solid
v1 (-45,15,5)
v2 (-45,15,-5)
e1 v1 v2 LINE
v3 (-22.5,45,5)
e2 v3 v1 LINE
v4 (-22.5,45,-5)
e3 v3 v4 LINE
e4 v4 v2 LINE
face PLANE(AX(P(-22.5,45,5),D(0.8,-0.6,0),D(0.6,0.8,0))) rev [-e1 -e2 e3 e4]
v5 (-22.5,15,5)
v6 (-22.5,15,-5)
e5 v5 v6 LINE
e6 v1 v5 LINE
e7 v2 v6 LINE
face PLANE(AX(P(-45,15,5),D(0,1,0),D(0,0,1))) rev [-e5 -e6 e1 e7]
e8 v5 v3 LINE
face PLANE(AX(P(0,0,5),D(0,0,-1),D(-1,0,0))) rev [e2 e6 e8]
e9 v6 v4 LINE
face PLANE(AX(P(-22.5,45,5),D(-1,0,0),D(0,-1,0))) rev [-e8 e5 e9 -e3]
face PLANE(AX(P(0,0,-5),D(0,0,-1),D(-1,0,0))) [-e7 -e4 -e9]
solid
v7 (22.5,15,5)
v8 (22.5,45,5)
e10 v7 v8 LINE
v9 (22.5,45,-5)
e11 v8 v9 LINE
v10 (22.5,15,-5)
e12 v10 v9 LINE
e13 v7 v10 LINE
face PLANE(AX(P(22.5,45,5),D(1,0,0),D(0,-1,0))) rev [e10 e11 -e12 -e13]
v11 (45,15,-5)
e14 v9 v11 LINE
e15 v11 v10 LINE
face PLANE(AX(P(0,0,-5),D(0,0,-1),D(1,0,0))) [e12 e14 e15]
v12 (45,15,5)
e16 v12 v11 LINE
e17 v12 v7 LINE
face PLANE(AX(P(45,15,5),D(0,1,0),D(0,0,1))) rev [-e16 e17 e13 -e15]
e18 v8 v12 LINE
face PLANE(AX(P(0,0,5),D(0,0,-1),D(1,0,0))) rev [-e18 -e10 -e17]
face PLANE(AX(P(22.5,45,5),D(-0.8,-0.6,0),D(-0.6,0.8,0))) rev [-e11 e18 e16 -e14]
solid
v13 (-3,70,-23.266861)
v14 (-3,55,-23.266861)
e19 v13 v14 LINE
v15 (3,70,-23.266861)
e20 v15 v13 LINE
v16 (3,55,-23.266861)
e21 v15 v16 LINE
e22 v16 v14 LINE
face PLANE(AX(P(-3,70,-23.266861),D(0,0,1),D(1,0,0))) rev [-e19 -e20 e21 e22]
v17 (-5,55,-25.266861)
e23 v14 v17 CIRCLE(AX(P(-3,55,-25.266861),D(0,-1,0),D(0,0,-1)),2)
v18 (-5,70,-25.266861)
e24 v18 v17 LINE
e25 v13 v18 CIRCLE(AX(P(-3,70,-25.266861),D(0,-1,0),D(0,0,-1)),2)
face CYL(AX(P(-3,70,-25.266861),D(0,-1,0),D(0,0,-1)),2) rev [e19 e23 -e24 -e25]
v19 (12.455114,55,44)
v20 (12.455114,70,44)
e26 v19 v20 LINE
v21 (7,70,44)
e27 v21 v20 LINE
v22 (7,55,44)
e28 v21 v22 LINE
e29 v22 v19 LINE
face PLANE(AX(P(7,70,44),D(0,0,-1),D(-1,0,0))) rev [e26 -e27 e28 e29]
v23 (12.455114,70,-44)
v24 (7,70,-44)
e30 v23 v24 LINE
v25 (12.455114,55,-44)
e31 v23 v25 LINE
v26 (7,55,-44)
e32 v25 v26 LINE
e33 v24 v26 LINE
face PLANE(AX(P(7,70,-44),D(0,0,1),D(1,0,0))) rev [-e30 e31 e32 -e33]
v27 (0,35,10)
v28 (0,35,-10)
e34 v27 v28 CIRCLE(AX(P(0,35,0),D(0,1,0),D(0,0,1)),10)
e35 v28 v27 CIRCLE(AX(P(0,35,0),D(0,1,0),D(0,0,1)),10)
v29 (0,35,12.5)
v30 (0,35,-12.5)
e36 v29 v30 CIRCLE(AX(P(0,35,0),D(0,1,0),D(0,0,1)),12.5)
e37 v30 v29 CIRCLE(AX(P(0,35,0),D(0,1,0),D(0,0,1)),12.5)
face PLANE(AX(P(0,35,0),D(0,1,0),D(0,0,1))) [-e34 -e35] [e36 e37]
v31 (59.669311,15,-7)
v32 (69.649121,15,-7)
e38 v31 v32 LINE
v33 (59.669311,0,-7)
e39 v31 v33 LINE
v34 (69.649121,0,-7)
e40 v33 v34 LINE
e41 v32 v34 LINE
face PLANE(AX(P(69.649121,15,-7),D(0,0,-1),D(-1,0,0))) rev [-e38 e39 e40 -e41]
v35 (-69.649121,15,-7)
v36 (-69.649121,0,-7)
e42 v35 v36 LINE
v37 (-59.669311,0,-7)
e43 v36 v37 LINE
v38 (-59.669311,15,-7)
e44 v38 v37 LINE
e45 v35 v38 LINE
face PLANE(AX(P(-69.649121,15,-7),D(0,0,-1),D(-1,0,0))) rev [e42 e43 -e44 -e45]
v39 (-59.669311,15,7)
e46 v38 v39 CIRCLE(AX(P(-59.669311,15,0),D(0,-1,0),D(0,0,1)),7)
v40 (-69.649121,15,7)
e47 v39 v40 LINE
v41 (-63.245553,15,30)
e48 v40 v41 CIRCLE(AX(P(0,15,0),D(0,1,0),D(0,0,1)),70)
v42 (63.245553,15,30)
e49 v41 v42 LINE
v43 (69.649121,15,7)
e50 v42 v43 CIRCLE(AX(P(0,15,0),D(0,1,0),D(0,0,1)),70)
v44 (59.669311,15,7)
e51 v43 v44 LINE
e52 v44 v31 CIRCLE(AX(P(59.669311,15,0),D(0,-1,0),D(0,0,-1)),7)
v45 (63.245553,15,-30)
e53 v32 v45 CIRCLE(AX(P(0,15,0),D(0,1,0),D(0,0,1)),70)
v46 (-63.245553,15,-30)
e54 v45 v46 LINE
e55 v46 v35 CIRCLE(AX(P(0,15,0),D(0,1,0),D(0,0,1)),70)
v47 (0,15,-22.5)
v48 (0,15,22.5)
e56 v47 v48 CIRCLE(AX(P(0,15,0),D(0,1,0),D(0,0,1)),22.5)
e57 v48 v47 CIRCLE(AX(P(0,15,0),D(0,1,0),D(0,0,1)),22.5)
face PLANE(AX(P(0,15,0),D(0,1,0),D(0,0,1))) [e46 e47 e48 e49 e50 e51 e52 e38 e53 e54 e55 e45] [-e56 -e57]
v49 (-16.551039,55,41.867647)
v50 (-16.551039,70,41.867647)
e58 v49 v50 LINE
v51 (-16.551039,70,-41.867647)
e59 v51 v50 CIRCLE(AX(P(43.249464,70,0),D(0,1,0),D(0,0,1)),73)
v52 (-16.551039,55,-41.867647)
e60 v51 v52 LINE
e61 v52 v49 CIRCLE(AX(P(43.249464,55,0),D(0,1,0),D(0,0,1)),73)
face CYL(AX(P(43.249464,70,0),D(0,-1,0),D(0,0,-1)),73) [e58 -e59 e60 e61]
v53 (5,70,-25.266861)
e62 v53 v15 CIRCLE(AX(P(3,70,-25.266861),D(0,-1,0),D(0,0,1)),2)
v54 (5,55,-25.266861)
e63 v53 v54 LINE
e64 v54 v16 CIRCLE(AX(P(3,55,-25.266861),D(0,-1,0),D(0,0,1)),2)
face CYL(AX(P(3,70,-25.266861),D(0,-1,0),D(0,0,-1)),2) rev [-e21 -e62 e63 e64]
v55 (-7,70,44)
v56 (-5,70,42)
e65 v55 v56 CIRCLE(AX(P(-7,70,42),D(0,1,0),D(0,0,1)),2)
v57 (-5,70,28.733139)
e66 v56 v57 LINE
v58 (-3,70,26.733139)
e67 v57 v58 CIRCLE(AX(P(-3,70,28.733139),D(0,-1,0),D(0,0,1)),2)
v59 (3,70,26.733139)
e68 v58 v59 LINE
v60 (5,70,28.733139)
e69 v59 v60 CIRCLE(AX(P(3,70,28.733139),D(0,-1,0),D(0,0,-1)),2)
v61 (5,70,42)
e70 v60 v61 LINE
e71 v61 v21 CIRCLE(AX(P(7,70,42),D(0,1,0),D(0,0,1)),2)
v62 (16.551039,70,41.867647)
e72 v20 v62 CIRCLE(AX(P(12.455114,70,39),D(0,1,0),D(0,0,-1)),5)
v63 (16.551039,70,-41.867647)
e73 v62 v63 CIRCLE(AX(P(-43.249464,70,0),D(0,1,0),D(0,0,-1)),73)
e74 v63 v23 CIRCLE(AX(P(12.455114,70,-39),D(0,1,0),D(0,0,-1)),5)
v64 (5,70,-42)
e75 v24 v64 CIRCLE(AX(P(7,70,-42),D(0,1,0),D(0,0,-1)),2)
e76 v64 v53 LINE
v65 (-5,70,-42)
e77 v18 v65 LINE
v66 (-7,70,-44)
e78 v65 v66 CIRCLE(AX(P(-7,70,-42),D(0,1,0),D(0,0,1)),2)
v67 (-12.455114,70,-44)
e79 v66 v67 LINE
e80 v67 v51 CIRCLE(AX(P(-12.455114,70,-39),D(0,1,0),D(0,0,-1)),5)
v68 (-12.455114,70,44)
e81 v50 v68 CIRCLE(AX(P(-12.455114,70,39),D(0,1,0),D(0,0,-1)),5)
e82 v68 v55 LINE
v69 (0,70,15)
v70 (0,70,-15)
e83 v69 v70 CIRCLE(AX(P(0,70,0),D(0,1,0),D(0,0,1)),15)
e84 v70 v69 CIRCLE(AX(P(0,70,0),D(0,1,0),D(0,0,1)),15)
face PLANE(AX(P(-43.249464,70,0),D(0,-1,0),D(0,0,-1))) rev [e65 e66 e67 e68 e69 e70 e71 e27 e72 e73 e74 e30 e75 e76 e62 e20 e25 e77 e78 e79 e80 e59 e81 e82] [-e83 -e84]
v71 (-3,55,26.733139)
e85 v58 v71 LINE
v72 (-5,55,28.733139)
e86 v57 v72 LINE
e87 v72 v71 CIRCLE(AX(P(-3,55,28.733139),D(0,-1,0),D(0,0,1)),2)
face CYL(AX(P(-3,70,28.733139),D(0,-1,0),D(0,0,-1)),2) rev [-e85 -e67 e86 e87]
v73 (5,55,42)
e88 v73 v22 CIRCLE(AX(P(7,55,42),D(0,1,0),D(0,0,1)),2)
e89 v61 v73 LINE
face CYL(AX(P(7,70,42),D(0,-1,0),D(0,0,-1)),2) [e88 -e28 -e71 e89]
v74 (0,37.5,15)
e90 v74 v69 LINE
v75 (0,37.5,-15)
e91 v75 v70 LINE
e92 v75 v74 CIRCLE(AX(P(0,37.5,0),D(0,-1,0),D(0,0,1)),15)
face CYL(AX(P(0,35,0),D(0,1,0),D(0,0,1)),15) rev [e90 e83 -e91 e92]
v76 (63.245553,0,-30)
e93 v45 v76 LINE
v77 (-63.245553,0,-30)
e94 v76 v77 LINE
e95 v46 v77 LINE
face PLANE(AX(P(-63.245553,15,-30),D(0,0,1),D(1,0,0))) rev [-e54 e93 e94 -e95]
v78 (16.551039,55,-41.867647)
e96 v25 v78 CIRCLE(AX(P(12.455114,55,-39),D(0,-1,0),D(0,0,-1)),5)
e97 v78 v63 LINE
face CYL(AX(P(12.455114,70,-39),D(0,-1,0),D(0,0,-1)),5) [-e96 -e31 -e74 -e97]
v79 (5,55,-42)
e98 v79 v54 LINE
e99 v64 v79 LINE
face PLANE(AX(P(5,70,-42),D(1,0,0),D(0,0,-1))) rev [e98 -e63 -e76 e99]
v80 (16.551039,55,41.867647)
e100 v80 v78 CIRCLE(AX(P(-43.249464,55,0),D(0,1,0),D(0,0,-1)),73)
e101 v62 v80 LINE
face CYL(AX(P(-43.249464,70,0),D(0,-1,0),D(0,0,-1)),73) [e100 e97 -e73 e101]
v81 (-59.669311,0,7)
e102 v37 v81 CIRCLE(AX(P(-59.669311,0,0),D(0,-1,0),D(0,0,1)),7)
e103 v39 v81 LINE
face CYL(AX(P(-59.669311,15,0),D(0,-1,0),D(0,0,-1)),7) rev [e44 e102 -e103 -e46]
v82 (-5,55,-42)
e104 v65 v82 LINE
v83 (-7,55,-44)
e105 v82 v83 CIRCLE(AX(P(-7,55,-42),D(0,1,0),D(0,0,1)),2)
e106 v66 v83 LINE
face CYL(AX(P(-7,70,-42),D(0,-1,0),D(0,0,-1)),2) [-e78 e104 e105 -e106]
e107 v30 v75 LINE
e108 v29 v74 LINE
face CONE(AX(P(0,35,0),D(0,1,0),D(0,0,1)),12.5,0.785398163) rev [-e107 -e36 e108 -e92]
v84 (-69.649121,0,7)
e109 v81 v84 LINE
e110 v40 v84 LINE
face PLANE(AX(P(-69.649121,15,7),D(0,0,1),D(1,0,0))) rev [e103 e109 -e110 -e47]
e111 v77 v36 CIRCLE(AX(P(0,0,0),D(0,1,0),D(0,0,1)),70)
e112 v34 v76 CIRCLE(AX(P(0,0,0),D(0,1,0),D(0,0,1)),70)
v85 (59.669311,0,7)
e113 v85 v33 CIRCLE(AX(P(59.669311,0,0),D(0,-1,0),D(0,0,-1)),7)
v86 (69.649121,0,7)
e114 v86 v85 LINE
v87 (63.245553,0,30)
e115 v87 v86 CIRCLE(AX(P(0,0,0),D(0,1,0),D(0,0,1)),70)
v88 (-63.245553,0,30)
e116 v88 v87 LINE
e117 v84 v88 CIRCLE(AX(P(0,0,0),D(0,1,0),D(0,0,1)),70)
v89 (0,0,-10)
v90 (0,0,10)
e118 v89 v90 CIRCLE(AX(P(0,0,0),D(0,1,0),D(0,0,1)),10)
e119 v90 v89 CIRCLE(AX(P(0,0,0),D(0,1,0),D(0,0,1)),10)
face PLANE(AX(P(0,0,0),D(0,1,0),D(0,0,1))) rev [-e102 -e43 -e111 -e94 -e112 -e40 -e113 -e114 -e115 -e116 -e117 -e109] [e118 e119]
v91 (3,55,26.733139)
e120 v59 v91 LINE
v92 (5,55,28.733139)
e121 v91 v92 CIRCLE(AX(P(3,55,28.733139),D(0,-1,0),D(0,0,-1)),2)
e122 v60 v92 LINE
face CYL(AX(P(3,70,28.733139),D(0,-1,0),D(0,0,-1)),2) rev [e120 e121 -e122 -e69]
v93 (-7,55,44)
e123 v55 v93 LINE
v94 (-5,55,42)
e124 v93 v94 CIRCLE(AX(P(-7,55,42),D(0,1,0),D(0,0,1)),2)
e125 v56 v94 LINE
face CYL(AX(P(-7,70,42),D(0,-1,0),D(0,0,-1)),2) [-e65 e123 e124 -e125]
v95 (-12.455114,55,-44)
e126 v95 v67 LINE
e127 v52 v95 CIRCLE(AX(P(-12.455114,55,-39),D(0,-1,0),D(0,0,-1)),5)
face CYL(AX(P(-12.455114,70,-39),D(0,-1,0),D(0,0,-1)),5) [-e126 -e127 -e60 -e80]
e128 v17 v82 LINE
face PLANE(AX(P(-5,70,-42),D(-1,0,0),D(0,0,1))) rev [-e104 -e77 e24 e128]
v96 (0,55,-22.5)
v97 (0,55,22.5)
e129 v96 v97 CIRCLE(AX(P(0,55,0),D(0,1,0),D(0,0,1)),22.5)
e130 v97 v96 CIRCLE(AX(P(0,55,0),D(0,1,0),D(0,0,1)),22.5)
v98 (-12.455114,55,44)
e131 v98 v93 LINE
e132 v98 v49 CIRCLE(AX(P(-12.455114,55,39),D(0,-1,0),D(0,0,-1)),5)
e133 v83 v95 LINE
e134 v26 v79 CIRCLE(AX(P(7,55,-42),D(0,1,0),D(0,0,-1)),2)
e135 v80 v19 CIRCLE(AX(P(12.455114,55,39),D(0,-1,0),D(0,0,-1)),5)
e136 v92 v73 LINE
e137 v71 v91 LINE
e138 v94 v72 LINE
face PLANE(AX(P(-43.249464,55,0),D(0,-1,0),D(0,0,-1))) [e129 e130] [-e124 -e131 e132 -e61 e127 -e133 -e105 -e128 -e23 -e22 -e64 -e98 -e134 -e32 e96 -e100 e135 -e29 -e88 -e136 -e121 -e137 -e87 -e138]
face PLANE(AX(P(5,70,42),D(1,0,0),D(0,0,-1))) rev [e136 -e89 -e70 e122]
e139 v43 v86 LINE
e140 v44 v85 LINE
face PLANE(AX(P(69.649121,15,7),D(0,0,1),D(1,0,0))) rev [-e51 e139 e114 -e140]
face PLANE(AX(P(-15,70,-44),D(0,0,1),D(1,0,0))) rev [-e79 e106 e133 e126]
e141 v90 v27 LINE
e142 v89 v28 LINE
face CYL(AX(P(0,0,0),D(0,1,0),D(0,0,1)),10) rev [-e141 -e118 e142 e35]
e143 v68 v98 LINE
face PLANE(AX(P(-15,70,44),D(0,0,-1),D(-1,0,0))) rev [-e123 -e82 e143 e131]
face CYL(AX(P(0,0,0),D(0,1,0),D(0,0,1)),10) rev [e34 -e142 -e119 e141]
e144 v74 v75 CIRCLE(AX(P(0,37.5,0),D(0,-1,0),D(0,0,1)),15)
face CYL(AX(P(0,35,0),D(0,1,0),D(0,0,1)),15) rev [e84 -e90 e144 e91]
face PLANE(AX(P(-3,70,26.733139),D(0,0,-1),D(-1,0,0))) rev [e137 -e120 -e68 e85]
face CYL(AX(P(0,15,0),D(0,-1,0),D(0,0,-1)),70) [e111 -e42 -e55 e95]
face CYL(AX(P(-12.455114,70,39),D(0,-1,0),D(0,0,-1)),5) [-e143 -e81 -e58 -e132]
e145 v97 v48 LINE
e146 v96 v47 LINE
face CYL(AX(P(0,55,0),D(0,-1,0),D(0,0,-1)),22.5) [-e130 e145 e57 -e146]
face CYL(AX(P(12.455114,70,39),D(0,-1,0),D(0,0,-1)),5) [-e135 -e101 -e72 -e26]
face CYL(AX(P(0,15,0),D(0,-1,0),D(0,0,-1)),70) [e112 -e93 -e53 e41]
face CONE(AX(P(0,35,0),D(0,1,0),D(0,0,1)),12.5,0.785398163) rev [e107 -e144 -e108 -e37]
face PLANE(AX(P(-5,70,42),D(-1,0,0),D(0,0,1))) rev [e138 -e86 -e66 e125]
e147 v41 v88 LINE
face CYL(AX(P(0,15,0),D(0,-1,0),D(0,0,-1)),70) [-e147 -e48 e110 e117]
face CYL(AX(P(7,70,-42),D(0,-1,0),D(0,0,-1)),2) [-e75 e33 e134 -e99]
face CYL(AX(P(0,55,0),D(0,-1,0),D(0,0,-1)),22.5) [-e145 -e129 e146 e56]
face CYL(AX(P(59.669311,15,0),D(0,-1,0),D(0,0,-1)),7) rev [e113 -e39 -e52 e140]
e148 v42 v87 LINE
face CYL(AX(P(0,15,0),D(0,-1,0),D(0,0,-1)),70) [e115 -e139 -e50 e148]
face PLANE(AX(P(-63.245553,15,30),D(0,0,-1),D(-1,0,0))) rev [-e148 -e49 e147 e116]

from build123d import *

# Parameters (mm, degrees)
BASE_PLATE_DEPTH         = 15
BOSS_SKETCH_45_R         = 22.5
BOSS_45_DEPTH            = 40
TOP_FLANGE_DEPTH         = 15
COUNTERBORE_SKETCH_30_R  = 15
COUNTERBORE_30_DEPTH     = 35
THROUGH_BORE_SKETCH_20_R = 10
THROUGH_BORE_20_DEPTH    = 35
BORE_CHAMFER_2_5_SIZE    = 2.5
GUSSET_RIB_DEPTH         = 5
FLANGE_FILLETS_R5_R      = 5


with BuildPart() as part:
    # Base Plate Sketch → Base Plate (new body)
    with BuildSketch(Plane(origin=(0, 0, 0), x_dir=(1, 0, 0), z_dir=(0, 1, 0))):
        with BuildLine():
            Line((-69.649120597, 7), (-59.669311209, 7))
            ThreePointArc((-59.669311209, 7), (-52.669311209, 0), (-59.669311209, -7))
            Line((-59.669311209, -7), (-69.649120597, -7))
            ThreePointArc((-69.649120597, -7), (-67.435143517, -18.775021141), (-63.245553203, -30))
            Line((-63.245553203, -30), (63.245553203, -30))
            ThreePointArc((63.245553203, -30), (67.435143517, -18.775021141), (69.649120597, -7))
            Line((69.649120597, -7), (59.669311209, -7))
            ThreePointArc((59.669311209, -7), (52.669311209, 0), (59.669311209, 7))
            Line((59.669311209, 7), (69.649120597, 7))
            ThreePointArc((69.649120597, 7), (67.435143517, 18.775021141), (63.245553203, 30))
            Line((63.245553203, 30), (-63.245553203, 30))
            ThreePointArc((-63.245553203, 30), (-67.435143517, 18.775021141), (-69.649120597, 7))
        make_face()
    extrude(amount=BASE_PLATE_DEPTH)

    # Boss Sketch Ø45 → Boss Ø45 (add)
    with BuildSketch(Plane(origin=(0, 15, 0), x_dir=(1, 0, 0), z_dir=(0, 1, 0))):
        with Locations(Location((0, 0, 0), (0, 0, 270))):
            Circle(BOSS_SKETCH_45_R)
    extrude(amount=BOSS_45_DEPTH)

    # Top Flange Sketch → Top Flange (add)
    with BuildSketch(Plane(origin=(0, 55, 0), x_dir=(1, 0, 0), z_dir=(0, 1, 0))):
        with BuildLine():
            Line((7, -44), (15, -44))
            ThreePointArc((15, -44), (29.750536483, 0), (15, 44))
            Line((15, 44), (7, 44))
            ThreePointArc((7, 44), (5.585786438, 43.414213562), (5, 42))
            Line((5, 42), (5, 25.266861381))
            ThreePointArc((5, 25.266861381), (4.414213562, 23.852647819), (3, 23.266861381))
            Line((3, 23.266861381), (-3, 23.266861381))
            ThreePointArc((-3, 23.266861381), (-4.414213562, 23.852647819), (-5, 25.266861381))
            Line((-5, 25.266861381), (-5, 42))
            ThreePointArc((-5, 42), (-5.585786438, 43.414213562), (-7, 44))
            Line((-7, 44), (-15, 44))
            ThreePointArc((-15, 44), (-29.750536483, 0), (-15, -44))
            Line((-15, -44), (-7, -44))
            ThreePointArc((-7, -44), (-5.585786438, -43.414213562), (-5, -42))
            Line((-5, -42), (-5, -28.733138619))
            ThreePointArc((-5, -28.733138619), (-4.414213562, -27.318925056), (-3, -26.733138619))
            Line((-3, -26.733138619), (3, -26.733138619))
            ThreePointArc((3, -26.733138619), (4.414213562, -27.318925056), (5, -28.733138619))
            Line((5, -28.733138619), (5, -42))
            ThreePointArc((5, -42), (5.585786438, -43.414213562), (7, -44))
        make_face()
    extrude(amount=TOP_FLANGE_DEPTH)

    # Counterbore Sketch Ø30 → Counterbore Ø30 (cut)
    with BuildSketch(Plane(origin=(0, 70, 0), x_dir=(1, 0, 0), z_dir=(0, 1, 0))):
        with Locations(Location((0, 0, 0), (0, 0, 270))):
            Circle(COUNTERBORE_SKETCH_30_R)
    extrude(amount=-COUNTERBORE_30_DEPTH, mode=Mode.SUBTRACT)

    # Through Bore Sketch Ø20 → Through Bore Ø20 (cut)
    with BuildSketch(Plane(origin=(0, 35, 0), x_dir=(1, 0, 0), z_dir=(0, 1, 0))):
        with Locations(Location((0, 0, 0), (0, 0, 270))):
            Circle(THROUGH_BORE_SKETCH_20_R)
    extrude(amount=-THROUGH_BORE_20_DEPTH, mode=Mode.SUBTRACT)

    # Bore Chamfer 2.5
    bore_chamfer_2_5_edges = [part.edges().sort_by_distance(p)[0] for p in [
        (0, 35, -15),
    ]]
    chamfer(bore_chamfer_2_5_edges, length=BORE_CHAMFER_2_5_SIZE)

    # Flange Fillets R5
    flange_fillets_r5_edges = [part.edges().sort_by_distance(p)[0] for p in [
        (15, 62.5, 44),
        (15, 62.5, -44),
        (-15, 62.5, -44),
        (-15, 62.5, 44),
    ]]
    fillet(flange_fillets_r5_edges, radius=FLANGE_FILLETS_R5_R)


with BuildPart() as body_2:
    # Gusset Rib Sketch → Gusset Rib (new, symmetric)
    with BuildSketch(Plane.XY):
        Polygon((-22.5, 45), (-22.5, 15), (-45, 15), align=None)
    extrude(amount=GUSSET_RIB_DEPTH, both=True)


with BuildPart() as body_3:
    # Gusset Rib Mirror: mirrored copy
    add(body_2.part.mirror(Plane(origin=(0, 0, 0), x_dir=(0, 0, 1), z_dir=(1, 0, 0))))


solid = Compound([part.part, body_2.part, body_3.part])
